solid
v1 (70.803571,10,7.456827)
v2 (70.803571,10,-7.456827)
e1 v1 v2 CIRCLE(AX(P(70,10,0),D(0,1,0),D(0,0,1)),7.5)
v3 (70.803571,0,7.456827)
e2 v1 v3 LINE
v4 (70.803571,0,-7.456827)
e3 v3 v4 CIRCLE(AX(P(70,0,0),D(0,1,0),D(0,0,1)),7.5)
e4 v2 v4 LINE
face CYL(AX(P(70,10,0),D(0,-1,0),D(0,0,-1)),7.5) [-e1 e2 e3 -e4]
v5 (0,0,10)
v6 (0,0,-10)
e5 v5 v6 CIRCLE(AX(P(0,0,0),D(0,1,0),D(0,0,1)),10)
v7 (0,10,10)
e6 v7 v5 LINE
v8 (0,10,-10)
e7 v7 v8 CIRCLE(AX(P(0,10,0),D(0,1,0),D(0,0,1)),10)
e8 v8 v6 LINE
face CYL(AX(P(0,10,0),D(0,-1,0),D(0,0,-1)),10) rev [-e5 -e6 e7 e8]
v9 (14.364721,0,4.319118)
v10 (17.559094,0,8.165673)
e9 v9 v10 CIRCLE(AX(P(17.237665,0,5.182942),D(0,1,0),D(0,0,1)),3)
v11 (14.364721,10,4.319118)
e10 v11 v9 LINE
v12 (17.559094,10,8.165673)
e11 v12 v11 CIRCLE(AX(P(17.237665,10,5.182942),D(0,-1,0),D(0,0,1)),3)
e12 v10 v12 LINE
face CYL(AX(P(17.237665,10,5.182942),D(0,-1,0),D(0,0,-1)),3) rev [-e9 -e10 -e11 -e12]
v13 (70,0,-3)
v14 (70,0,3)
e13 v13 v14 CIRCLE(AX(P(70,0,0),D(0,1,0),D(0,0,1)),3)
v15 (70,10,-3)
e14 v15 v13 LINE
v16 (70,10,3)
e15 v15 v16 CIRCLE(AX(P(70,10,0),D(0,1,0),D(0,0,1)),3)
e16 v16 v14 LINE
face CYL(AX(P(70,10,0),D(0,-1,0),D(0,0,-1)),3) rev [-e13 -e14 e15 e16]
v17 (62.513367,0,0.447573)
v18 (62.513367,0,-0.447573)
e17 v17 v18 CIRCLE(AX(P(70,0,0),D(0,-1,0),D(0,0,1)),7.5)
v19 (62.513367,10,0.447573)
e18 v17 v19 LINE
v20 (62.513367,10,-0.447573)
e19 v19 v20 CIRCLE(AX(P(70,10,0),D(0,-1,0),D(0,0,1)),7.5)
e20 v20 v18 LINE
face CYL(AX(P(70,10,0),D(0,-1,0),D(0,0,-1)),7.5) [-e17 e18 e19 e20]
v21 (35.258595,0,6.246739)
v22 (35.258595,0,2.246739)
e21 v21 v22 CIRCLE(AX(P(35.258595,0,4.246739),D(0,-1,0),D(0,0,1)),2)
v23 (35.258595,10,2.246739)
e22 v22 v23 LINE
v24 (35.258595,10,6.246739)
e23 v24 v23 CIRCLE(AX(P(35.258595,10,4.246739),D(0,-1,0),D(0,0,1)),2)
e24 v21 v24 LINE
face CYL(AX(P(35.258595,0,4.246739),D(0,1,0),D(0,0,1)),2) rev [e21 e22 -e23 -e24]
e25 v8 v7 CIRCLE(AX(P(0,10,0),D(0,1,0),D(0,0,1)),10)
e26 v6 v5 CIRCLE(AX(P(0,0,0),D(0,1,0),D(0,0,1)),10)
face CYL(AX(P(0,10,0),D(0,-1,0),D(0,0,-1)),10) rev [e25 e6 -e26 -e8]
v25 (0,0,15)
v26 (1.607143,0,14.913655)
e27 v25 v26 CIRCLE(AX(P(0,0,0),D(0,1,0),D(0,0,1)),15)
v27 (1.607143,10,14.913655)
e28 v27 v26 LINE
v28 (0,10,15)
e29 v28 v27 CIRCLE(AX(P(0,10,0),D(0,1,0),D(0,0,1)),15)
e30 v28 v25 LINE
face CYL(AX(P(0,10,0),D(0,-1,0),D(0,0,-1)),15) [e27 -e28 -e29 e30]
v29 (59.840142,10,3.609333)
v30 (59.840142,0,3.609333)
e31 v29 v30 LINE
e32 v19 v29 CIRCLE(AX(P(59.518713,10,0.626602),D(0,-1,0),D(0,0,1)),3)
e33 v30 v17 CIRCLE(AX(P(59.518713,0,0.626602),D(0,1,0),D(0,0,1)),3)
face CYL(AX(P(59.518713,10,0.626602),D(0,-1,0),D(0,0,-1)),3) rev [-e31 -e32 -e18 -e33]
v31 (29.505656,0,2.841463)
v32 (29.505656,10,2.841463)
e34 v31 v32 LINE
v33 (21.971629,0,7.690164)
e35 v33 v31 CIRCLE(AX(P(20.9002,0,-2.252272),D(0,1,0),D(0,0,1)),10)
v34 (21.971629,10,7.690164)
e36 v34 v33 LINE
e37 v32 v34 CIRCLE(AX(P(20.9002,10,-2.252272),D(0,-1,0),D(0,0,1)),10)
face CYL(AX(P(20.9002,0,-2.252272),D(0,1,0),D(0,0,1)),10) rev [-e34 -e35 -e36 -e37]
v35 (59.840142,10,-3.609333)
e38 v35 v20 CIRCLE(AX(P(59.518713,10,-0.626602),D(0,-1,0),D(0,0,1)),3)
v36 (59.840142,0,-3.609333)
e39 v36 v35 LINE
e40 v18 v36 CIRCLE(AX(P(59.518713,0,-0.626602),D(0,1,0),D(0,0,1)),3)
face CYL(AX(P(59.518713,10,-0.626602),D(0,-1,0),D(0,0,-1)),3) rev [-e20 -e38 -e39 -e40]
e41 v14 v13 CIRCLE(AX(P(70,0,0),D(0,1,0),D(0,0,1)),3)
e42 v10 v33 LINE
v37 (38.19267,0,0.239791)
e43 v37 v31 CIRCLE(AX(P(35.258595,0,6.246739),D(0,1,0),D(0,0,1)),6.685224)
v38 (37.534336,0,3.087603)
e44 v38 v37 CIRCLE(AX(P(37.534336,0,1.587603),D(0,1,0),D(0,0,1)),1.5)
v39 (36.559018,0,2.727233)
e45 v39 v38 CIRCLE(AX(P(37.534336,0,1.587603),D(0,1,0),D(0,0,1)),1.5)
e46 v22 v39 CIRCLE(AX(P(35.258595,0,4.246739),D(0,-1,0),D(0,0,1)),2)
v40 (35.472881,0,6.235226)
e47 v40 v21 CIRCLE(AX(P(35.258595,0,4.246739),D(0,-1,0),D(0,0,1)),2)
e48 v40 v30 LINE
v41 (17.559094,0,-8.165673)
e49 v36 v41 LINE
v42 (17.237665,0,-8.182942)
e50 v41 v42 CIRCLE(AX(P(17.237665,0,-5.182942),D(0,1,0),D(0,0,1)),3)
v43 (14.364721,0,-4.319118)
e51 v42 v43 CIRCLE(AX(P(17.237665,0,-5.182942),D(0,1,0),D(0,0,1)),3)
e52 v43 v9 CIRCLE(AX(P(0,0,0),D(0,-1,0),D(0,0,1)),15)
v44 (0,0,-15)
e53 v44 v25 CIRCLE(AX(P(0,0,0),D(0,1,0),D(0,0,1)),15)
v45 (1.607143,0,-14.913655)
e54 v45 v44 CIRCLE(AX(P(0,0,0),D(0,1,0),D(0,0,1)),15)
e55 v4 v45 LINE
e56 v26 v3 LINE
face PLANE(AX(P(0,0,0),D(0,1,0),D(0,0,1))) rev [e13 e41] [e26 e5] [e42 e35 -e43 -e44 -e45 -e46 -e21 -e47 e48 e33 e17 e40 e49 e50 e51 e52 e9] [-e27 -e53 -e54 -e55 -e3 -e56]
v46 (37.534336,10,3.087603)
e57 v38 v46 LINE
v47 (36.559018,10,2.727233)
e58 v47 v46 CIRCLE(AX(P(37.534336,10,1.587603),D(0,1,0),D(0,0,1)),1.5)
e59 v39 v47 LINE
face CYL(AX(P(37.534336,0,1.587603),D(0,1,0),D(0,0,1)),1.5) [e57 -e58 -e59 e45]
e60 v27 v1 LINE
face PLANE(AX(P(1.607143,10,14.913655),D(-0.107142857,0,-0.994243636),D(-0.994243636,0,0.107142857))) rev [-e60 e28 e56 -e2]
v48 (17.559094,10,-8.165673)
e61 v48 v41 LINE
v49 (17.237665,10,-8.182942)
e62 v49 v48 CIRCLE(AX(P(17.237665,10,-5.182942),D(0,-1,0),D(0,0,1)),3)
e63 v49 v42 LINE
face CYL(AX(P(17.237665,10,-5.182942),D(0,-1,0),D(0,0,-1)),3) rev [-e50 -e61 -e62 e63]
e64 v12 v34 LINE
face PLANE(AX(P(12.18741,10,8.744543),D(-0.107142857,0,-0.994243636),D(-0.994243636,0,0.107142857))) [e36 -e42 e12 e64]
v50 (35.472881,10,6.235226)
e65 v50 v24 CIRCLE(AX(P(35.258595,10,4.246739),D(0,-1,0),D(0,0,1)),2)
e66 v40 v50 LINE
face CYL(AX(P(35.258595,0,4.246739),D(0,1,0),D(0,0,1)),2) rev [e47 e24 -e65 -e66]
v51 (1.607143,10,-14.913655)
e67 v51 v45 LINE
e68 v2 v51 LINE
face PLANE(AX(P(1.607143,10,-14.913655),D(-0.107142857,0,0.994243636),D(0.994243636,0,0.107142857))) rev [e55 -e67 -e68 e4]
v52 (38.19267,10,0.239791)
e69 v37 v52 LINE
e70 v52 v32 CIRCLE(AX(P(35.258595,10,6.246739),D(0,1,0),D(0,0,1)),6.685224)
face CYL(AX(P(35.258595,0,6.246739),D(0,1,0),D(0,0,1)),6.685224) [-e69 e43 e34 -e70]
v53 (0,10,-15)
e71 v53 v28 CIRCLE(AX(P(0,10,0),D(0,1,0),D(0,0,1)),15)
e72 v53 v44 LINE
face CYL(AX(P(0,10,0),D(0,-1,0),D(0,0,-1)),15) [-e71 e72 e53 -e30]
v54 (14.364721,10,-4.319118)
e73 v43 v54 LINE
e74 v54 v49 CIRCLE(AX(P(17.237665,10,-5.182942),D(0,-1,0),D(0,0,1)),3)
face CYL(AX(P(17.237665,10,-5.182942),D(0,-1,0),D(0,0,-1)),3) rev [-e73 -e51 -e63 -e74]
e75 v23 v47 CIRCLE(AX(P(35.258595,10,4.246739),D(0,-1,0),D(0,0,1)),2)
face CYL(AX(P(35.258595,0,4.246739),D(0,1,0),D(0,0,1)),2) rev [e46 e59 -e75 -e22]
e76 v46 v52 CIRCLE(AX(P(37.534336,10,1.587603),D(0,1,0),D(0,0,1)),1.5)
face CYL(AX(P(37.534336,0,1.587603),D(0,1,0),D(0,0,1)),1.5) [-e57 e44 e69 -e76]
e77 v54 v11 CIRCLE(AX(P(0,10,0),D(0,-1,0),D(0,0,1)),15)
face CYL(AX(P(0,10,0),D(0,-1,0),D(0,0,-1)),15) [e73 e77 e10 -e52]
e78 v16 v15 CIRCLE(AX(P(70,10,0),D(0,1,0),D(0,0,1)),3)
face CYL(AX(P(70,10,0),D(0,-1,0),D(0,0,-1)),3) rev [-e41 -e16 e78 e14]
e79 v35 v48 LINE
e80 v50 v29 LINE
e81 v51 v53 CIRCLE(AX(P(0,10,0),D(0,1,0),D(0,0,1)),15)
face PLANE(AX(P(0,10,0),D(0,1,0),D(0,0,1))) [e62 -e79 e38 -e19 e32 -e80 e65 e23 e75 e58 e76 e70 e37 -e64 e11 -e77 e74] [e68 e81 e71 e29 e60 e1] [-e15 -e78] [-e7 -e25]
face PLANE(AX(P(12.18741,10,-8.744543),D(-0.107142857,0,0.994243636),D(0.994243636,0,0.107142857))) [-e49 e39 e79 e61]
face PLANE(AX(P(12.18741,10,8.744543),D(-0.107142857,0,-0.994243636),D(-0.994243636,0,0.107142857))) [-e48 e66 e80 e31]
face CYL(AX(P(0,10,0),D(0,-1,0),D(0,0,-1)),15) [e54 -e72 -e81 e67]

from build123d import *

# Parameters (mm, degrees)
SKETCH_1_R      = 10
SKETCH_1_R_2    = 3
EXTRUDE_1_DEPTH = 10
FILLET_1_R      = 3
EXTRUDE_3_DEPTH = 10
FILLET_3_R      = 10


with BuildPart() as part:
    # 草图1 → 凸台-拉伸1 (new body)
    with BuildSketch(Plane(origin=(0, 0, 0), x_dir=(1, 0, 0), z_dir=(0, 1, 0))):
        with BuildLine():
            Line((1.607142857, 14.913654543), (70.803571429, 7.456827272))
            ThreePointArc((70.803571429, 7.456827272), (77.5, 0), (70.803571429, -7.456827272))
            Line((70.803571429, -7.456827272), (1.607142857, -14.913654543))
            ThreePointArc((1.607142857, -14.913654543), (-15, 0), (1.607142857, 14.913654543))
        make_face()
        with Locations(Location((0, 0, 0), (0, 0, 270))):
            Circle(SKETCH_1_R, mode=Mode.SUBTRACT)
        with Locations(Location((70, 0, 0), (0, 0, 270))):
            Circle(SKETCH_1_R_2, mode=Mode.SUBTRACT)
        with BuildLine():
            Line((12.187410355, 8.744542803), (63.23749297, 3.243223499))
            ThreePointArc((63.23749297, 3.243223499), (62.5, 0), (63.23749297, -3.243223499))
            Line((63.23749297, -3.243223499), (12.187410355, -8.744542803))
            ThreePointArc((12.187410355, -8.744542803), (15, 0), (12.187410355, 8.744542803))
        make_face(mode=Mode.SUBTRACT)
    extrude(amount=EXTRUDE_1_DEPTH)

    # 圆角1
    fillet_1_edges = [part.edges().sort_by_distance(p)[0] for p in [
        (12.187410355, 5, -8.744542803),
        (12.187410355, 5, 8.744542803),
        (63.23749297, 5, 3.243223499),
        (63.23749297, 5, -3.243223499),
    ]]
    fillet(fillet_1_edges, radius=FILLET_1_R)

    # 草图3 → 凸台-拉伸3 (add)
    with BuildSketch(Plane(origin=(0, 10, 0), x_dir=(1, 0, 0), z_dir=(0, 1, 0))):
        with BuildLine():
            Line((28.613097425, -6.974458511), (35.472880926, -6.235226418))
            ThreePointArc((35.472880926, -6.235226418), (33.348074169, -3.655207792), (36.559018282, -2.727232699))
            ThreePointArc((36.559018282, -2.727232699), (38.788114159, -2.411034272), (38.192669869, -0.239791316))
            ThreePointArc((38.192669869, -0.239791316), (31.413780396, -0.777770747), (28.613097425, -6.974458511))
        make_face()
    extrude(amount=-EXTRUDE_3_DEPTH)

    # 圆角3
    fillet_3_edges = [part.edges().sort_by_distance(p)[0] for p in [
        (28.613097425, 5, 6.974458511),
    ]]
    fillet(fillet_3_edges, radius=FILLET_3_R)


solid = part.part
